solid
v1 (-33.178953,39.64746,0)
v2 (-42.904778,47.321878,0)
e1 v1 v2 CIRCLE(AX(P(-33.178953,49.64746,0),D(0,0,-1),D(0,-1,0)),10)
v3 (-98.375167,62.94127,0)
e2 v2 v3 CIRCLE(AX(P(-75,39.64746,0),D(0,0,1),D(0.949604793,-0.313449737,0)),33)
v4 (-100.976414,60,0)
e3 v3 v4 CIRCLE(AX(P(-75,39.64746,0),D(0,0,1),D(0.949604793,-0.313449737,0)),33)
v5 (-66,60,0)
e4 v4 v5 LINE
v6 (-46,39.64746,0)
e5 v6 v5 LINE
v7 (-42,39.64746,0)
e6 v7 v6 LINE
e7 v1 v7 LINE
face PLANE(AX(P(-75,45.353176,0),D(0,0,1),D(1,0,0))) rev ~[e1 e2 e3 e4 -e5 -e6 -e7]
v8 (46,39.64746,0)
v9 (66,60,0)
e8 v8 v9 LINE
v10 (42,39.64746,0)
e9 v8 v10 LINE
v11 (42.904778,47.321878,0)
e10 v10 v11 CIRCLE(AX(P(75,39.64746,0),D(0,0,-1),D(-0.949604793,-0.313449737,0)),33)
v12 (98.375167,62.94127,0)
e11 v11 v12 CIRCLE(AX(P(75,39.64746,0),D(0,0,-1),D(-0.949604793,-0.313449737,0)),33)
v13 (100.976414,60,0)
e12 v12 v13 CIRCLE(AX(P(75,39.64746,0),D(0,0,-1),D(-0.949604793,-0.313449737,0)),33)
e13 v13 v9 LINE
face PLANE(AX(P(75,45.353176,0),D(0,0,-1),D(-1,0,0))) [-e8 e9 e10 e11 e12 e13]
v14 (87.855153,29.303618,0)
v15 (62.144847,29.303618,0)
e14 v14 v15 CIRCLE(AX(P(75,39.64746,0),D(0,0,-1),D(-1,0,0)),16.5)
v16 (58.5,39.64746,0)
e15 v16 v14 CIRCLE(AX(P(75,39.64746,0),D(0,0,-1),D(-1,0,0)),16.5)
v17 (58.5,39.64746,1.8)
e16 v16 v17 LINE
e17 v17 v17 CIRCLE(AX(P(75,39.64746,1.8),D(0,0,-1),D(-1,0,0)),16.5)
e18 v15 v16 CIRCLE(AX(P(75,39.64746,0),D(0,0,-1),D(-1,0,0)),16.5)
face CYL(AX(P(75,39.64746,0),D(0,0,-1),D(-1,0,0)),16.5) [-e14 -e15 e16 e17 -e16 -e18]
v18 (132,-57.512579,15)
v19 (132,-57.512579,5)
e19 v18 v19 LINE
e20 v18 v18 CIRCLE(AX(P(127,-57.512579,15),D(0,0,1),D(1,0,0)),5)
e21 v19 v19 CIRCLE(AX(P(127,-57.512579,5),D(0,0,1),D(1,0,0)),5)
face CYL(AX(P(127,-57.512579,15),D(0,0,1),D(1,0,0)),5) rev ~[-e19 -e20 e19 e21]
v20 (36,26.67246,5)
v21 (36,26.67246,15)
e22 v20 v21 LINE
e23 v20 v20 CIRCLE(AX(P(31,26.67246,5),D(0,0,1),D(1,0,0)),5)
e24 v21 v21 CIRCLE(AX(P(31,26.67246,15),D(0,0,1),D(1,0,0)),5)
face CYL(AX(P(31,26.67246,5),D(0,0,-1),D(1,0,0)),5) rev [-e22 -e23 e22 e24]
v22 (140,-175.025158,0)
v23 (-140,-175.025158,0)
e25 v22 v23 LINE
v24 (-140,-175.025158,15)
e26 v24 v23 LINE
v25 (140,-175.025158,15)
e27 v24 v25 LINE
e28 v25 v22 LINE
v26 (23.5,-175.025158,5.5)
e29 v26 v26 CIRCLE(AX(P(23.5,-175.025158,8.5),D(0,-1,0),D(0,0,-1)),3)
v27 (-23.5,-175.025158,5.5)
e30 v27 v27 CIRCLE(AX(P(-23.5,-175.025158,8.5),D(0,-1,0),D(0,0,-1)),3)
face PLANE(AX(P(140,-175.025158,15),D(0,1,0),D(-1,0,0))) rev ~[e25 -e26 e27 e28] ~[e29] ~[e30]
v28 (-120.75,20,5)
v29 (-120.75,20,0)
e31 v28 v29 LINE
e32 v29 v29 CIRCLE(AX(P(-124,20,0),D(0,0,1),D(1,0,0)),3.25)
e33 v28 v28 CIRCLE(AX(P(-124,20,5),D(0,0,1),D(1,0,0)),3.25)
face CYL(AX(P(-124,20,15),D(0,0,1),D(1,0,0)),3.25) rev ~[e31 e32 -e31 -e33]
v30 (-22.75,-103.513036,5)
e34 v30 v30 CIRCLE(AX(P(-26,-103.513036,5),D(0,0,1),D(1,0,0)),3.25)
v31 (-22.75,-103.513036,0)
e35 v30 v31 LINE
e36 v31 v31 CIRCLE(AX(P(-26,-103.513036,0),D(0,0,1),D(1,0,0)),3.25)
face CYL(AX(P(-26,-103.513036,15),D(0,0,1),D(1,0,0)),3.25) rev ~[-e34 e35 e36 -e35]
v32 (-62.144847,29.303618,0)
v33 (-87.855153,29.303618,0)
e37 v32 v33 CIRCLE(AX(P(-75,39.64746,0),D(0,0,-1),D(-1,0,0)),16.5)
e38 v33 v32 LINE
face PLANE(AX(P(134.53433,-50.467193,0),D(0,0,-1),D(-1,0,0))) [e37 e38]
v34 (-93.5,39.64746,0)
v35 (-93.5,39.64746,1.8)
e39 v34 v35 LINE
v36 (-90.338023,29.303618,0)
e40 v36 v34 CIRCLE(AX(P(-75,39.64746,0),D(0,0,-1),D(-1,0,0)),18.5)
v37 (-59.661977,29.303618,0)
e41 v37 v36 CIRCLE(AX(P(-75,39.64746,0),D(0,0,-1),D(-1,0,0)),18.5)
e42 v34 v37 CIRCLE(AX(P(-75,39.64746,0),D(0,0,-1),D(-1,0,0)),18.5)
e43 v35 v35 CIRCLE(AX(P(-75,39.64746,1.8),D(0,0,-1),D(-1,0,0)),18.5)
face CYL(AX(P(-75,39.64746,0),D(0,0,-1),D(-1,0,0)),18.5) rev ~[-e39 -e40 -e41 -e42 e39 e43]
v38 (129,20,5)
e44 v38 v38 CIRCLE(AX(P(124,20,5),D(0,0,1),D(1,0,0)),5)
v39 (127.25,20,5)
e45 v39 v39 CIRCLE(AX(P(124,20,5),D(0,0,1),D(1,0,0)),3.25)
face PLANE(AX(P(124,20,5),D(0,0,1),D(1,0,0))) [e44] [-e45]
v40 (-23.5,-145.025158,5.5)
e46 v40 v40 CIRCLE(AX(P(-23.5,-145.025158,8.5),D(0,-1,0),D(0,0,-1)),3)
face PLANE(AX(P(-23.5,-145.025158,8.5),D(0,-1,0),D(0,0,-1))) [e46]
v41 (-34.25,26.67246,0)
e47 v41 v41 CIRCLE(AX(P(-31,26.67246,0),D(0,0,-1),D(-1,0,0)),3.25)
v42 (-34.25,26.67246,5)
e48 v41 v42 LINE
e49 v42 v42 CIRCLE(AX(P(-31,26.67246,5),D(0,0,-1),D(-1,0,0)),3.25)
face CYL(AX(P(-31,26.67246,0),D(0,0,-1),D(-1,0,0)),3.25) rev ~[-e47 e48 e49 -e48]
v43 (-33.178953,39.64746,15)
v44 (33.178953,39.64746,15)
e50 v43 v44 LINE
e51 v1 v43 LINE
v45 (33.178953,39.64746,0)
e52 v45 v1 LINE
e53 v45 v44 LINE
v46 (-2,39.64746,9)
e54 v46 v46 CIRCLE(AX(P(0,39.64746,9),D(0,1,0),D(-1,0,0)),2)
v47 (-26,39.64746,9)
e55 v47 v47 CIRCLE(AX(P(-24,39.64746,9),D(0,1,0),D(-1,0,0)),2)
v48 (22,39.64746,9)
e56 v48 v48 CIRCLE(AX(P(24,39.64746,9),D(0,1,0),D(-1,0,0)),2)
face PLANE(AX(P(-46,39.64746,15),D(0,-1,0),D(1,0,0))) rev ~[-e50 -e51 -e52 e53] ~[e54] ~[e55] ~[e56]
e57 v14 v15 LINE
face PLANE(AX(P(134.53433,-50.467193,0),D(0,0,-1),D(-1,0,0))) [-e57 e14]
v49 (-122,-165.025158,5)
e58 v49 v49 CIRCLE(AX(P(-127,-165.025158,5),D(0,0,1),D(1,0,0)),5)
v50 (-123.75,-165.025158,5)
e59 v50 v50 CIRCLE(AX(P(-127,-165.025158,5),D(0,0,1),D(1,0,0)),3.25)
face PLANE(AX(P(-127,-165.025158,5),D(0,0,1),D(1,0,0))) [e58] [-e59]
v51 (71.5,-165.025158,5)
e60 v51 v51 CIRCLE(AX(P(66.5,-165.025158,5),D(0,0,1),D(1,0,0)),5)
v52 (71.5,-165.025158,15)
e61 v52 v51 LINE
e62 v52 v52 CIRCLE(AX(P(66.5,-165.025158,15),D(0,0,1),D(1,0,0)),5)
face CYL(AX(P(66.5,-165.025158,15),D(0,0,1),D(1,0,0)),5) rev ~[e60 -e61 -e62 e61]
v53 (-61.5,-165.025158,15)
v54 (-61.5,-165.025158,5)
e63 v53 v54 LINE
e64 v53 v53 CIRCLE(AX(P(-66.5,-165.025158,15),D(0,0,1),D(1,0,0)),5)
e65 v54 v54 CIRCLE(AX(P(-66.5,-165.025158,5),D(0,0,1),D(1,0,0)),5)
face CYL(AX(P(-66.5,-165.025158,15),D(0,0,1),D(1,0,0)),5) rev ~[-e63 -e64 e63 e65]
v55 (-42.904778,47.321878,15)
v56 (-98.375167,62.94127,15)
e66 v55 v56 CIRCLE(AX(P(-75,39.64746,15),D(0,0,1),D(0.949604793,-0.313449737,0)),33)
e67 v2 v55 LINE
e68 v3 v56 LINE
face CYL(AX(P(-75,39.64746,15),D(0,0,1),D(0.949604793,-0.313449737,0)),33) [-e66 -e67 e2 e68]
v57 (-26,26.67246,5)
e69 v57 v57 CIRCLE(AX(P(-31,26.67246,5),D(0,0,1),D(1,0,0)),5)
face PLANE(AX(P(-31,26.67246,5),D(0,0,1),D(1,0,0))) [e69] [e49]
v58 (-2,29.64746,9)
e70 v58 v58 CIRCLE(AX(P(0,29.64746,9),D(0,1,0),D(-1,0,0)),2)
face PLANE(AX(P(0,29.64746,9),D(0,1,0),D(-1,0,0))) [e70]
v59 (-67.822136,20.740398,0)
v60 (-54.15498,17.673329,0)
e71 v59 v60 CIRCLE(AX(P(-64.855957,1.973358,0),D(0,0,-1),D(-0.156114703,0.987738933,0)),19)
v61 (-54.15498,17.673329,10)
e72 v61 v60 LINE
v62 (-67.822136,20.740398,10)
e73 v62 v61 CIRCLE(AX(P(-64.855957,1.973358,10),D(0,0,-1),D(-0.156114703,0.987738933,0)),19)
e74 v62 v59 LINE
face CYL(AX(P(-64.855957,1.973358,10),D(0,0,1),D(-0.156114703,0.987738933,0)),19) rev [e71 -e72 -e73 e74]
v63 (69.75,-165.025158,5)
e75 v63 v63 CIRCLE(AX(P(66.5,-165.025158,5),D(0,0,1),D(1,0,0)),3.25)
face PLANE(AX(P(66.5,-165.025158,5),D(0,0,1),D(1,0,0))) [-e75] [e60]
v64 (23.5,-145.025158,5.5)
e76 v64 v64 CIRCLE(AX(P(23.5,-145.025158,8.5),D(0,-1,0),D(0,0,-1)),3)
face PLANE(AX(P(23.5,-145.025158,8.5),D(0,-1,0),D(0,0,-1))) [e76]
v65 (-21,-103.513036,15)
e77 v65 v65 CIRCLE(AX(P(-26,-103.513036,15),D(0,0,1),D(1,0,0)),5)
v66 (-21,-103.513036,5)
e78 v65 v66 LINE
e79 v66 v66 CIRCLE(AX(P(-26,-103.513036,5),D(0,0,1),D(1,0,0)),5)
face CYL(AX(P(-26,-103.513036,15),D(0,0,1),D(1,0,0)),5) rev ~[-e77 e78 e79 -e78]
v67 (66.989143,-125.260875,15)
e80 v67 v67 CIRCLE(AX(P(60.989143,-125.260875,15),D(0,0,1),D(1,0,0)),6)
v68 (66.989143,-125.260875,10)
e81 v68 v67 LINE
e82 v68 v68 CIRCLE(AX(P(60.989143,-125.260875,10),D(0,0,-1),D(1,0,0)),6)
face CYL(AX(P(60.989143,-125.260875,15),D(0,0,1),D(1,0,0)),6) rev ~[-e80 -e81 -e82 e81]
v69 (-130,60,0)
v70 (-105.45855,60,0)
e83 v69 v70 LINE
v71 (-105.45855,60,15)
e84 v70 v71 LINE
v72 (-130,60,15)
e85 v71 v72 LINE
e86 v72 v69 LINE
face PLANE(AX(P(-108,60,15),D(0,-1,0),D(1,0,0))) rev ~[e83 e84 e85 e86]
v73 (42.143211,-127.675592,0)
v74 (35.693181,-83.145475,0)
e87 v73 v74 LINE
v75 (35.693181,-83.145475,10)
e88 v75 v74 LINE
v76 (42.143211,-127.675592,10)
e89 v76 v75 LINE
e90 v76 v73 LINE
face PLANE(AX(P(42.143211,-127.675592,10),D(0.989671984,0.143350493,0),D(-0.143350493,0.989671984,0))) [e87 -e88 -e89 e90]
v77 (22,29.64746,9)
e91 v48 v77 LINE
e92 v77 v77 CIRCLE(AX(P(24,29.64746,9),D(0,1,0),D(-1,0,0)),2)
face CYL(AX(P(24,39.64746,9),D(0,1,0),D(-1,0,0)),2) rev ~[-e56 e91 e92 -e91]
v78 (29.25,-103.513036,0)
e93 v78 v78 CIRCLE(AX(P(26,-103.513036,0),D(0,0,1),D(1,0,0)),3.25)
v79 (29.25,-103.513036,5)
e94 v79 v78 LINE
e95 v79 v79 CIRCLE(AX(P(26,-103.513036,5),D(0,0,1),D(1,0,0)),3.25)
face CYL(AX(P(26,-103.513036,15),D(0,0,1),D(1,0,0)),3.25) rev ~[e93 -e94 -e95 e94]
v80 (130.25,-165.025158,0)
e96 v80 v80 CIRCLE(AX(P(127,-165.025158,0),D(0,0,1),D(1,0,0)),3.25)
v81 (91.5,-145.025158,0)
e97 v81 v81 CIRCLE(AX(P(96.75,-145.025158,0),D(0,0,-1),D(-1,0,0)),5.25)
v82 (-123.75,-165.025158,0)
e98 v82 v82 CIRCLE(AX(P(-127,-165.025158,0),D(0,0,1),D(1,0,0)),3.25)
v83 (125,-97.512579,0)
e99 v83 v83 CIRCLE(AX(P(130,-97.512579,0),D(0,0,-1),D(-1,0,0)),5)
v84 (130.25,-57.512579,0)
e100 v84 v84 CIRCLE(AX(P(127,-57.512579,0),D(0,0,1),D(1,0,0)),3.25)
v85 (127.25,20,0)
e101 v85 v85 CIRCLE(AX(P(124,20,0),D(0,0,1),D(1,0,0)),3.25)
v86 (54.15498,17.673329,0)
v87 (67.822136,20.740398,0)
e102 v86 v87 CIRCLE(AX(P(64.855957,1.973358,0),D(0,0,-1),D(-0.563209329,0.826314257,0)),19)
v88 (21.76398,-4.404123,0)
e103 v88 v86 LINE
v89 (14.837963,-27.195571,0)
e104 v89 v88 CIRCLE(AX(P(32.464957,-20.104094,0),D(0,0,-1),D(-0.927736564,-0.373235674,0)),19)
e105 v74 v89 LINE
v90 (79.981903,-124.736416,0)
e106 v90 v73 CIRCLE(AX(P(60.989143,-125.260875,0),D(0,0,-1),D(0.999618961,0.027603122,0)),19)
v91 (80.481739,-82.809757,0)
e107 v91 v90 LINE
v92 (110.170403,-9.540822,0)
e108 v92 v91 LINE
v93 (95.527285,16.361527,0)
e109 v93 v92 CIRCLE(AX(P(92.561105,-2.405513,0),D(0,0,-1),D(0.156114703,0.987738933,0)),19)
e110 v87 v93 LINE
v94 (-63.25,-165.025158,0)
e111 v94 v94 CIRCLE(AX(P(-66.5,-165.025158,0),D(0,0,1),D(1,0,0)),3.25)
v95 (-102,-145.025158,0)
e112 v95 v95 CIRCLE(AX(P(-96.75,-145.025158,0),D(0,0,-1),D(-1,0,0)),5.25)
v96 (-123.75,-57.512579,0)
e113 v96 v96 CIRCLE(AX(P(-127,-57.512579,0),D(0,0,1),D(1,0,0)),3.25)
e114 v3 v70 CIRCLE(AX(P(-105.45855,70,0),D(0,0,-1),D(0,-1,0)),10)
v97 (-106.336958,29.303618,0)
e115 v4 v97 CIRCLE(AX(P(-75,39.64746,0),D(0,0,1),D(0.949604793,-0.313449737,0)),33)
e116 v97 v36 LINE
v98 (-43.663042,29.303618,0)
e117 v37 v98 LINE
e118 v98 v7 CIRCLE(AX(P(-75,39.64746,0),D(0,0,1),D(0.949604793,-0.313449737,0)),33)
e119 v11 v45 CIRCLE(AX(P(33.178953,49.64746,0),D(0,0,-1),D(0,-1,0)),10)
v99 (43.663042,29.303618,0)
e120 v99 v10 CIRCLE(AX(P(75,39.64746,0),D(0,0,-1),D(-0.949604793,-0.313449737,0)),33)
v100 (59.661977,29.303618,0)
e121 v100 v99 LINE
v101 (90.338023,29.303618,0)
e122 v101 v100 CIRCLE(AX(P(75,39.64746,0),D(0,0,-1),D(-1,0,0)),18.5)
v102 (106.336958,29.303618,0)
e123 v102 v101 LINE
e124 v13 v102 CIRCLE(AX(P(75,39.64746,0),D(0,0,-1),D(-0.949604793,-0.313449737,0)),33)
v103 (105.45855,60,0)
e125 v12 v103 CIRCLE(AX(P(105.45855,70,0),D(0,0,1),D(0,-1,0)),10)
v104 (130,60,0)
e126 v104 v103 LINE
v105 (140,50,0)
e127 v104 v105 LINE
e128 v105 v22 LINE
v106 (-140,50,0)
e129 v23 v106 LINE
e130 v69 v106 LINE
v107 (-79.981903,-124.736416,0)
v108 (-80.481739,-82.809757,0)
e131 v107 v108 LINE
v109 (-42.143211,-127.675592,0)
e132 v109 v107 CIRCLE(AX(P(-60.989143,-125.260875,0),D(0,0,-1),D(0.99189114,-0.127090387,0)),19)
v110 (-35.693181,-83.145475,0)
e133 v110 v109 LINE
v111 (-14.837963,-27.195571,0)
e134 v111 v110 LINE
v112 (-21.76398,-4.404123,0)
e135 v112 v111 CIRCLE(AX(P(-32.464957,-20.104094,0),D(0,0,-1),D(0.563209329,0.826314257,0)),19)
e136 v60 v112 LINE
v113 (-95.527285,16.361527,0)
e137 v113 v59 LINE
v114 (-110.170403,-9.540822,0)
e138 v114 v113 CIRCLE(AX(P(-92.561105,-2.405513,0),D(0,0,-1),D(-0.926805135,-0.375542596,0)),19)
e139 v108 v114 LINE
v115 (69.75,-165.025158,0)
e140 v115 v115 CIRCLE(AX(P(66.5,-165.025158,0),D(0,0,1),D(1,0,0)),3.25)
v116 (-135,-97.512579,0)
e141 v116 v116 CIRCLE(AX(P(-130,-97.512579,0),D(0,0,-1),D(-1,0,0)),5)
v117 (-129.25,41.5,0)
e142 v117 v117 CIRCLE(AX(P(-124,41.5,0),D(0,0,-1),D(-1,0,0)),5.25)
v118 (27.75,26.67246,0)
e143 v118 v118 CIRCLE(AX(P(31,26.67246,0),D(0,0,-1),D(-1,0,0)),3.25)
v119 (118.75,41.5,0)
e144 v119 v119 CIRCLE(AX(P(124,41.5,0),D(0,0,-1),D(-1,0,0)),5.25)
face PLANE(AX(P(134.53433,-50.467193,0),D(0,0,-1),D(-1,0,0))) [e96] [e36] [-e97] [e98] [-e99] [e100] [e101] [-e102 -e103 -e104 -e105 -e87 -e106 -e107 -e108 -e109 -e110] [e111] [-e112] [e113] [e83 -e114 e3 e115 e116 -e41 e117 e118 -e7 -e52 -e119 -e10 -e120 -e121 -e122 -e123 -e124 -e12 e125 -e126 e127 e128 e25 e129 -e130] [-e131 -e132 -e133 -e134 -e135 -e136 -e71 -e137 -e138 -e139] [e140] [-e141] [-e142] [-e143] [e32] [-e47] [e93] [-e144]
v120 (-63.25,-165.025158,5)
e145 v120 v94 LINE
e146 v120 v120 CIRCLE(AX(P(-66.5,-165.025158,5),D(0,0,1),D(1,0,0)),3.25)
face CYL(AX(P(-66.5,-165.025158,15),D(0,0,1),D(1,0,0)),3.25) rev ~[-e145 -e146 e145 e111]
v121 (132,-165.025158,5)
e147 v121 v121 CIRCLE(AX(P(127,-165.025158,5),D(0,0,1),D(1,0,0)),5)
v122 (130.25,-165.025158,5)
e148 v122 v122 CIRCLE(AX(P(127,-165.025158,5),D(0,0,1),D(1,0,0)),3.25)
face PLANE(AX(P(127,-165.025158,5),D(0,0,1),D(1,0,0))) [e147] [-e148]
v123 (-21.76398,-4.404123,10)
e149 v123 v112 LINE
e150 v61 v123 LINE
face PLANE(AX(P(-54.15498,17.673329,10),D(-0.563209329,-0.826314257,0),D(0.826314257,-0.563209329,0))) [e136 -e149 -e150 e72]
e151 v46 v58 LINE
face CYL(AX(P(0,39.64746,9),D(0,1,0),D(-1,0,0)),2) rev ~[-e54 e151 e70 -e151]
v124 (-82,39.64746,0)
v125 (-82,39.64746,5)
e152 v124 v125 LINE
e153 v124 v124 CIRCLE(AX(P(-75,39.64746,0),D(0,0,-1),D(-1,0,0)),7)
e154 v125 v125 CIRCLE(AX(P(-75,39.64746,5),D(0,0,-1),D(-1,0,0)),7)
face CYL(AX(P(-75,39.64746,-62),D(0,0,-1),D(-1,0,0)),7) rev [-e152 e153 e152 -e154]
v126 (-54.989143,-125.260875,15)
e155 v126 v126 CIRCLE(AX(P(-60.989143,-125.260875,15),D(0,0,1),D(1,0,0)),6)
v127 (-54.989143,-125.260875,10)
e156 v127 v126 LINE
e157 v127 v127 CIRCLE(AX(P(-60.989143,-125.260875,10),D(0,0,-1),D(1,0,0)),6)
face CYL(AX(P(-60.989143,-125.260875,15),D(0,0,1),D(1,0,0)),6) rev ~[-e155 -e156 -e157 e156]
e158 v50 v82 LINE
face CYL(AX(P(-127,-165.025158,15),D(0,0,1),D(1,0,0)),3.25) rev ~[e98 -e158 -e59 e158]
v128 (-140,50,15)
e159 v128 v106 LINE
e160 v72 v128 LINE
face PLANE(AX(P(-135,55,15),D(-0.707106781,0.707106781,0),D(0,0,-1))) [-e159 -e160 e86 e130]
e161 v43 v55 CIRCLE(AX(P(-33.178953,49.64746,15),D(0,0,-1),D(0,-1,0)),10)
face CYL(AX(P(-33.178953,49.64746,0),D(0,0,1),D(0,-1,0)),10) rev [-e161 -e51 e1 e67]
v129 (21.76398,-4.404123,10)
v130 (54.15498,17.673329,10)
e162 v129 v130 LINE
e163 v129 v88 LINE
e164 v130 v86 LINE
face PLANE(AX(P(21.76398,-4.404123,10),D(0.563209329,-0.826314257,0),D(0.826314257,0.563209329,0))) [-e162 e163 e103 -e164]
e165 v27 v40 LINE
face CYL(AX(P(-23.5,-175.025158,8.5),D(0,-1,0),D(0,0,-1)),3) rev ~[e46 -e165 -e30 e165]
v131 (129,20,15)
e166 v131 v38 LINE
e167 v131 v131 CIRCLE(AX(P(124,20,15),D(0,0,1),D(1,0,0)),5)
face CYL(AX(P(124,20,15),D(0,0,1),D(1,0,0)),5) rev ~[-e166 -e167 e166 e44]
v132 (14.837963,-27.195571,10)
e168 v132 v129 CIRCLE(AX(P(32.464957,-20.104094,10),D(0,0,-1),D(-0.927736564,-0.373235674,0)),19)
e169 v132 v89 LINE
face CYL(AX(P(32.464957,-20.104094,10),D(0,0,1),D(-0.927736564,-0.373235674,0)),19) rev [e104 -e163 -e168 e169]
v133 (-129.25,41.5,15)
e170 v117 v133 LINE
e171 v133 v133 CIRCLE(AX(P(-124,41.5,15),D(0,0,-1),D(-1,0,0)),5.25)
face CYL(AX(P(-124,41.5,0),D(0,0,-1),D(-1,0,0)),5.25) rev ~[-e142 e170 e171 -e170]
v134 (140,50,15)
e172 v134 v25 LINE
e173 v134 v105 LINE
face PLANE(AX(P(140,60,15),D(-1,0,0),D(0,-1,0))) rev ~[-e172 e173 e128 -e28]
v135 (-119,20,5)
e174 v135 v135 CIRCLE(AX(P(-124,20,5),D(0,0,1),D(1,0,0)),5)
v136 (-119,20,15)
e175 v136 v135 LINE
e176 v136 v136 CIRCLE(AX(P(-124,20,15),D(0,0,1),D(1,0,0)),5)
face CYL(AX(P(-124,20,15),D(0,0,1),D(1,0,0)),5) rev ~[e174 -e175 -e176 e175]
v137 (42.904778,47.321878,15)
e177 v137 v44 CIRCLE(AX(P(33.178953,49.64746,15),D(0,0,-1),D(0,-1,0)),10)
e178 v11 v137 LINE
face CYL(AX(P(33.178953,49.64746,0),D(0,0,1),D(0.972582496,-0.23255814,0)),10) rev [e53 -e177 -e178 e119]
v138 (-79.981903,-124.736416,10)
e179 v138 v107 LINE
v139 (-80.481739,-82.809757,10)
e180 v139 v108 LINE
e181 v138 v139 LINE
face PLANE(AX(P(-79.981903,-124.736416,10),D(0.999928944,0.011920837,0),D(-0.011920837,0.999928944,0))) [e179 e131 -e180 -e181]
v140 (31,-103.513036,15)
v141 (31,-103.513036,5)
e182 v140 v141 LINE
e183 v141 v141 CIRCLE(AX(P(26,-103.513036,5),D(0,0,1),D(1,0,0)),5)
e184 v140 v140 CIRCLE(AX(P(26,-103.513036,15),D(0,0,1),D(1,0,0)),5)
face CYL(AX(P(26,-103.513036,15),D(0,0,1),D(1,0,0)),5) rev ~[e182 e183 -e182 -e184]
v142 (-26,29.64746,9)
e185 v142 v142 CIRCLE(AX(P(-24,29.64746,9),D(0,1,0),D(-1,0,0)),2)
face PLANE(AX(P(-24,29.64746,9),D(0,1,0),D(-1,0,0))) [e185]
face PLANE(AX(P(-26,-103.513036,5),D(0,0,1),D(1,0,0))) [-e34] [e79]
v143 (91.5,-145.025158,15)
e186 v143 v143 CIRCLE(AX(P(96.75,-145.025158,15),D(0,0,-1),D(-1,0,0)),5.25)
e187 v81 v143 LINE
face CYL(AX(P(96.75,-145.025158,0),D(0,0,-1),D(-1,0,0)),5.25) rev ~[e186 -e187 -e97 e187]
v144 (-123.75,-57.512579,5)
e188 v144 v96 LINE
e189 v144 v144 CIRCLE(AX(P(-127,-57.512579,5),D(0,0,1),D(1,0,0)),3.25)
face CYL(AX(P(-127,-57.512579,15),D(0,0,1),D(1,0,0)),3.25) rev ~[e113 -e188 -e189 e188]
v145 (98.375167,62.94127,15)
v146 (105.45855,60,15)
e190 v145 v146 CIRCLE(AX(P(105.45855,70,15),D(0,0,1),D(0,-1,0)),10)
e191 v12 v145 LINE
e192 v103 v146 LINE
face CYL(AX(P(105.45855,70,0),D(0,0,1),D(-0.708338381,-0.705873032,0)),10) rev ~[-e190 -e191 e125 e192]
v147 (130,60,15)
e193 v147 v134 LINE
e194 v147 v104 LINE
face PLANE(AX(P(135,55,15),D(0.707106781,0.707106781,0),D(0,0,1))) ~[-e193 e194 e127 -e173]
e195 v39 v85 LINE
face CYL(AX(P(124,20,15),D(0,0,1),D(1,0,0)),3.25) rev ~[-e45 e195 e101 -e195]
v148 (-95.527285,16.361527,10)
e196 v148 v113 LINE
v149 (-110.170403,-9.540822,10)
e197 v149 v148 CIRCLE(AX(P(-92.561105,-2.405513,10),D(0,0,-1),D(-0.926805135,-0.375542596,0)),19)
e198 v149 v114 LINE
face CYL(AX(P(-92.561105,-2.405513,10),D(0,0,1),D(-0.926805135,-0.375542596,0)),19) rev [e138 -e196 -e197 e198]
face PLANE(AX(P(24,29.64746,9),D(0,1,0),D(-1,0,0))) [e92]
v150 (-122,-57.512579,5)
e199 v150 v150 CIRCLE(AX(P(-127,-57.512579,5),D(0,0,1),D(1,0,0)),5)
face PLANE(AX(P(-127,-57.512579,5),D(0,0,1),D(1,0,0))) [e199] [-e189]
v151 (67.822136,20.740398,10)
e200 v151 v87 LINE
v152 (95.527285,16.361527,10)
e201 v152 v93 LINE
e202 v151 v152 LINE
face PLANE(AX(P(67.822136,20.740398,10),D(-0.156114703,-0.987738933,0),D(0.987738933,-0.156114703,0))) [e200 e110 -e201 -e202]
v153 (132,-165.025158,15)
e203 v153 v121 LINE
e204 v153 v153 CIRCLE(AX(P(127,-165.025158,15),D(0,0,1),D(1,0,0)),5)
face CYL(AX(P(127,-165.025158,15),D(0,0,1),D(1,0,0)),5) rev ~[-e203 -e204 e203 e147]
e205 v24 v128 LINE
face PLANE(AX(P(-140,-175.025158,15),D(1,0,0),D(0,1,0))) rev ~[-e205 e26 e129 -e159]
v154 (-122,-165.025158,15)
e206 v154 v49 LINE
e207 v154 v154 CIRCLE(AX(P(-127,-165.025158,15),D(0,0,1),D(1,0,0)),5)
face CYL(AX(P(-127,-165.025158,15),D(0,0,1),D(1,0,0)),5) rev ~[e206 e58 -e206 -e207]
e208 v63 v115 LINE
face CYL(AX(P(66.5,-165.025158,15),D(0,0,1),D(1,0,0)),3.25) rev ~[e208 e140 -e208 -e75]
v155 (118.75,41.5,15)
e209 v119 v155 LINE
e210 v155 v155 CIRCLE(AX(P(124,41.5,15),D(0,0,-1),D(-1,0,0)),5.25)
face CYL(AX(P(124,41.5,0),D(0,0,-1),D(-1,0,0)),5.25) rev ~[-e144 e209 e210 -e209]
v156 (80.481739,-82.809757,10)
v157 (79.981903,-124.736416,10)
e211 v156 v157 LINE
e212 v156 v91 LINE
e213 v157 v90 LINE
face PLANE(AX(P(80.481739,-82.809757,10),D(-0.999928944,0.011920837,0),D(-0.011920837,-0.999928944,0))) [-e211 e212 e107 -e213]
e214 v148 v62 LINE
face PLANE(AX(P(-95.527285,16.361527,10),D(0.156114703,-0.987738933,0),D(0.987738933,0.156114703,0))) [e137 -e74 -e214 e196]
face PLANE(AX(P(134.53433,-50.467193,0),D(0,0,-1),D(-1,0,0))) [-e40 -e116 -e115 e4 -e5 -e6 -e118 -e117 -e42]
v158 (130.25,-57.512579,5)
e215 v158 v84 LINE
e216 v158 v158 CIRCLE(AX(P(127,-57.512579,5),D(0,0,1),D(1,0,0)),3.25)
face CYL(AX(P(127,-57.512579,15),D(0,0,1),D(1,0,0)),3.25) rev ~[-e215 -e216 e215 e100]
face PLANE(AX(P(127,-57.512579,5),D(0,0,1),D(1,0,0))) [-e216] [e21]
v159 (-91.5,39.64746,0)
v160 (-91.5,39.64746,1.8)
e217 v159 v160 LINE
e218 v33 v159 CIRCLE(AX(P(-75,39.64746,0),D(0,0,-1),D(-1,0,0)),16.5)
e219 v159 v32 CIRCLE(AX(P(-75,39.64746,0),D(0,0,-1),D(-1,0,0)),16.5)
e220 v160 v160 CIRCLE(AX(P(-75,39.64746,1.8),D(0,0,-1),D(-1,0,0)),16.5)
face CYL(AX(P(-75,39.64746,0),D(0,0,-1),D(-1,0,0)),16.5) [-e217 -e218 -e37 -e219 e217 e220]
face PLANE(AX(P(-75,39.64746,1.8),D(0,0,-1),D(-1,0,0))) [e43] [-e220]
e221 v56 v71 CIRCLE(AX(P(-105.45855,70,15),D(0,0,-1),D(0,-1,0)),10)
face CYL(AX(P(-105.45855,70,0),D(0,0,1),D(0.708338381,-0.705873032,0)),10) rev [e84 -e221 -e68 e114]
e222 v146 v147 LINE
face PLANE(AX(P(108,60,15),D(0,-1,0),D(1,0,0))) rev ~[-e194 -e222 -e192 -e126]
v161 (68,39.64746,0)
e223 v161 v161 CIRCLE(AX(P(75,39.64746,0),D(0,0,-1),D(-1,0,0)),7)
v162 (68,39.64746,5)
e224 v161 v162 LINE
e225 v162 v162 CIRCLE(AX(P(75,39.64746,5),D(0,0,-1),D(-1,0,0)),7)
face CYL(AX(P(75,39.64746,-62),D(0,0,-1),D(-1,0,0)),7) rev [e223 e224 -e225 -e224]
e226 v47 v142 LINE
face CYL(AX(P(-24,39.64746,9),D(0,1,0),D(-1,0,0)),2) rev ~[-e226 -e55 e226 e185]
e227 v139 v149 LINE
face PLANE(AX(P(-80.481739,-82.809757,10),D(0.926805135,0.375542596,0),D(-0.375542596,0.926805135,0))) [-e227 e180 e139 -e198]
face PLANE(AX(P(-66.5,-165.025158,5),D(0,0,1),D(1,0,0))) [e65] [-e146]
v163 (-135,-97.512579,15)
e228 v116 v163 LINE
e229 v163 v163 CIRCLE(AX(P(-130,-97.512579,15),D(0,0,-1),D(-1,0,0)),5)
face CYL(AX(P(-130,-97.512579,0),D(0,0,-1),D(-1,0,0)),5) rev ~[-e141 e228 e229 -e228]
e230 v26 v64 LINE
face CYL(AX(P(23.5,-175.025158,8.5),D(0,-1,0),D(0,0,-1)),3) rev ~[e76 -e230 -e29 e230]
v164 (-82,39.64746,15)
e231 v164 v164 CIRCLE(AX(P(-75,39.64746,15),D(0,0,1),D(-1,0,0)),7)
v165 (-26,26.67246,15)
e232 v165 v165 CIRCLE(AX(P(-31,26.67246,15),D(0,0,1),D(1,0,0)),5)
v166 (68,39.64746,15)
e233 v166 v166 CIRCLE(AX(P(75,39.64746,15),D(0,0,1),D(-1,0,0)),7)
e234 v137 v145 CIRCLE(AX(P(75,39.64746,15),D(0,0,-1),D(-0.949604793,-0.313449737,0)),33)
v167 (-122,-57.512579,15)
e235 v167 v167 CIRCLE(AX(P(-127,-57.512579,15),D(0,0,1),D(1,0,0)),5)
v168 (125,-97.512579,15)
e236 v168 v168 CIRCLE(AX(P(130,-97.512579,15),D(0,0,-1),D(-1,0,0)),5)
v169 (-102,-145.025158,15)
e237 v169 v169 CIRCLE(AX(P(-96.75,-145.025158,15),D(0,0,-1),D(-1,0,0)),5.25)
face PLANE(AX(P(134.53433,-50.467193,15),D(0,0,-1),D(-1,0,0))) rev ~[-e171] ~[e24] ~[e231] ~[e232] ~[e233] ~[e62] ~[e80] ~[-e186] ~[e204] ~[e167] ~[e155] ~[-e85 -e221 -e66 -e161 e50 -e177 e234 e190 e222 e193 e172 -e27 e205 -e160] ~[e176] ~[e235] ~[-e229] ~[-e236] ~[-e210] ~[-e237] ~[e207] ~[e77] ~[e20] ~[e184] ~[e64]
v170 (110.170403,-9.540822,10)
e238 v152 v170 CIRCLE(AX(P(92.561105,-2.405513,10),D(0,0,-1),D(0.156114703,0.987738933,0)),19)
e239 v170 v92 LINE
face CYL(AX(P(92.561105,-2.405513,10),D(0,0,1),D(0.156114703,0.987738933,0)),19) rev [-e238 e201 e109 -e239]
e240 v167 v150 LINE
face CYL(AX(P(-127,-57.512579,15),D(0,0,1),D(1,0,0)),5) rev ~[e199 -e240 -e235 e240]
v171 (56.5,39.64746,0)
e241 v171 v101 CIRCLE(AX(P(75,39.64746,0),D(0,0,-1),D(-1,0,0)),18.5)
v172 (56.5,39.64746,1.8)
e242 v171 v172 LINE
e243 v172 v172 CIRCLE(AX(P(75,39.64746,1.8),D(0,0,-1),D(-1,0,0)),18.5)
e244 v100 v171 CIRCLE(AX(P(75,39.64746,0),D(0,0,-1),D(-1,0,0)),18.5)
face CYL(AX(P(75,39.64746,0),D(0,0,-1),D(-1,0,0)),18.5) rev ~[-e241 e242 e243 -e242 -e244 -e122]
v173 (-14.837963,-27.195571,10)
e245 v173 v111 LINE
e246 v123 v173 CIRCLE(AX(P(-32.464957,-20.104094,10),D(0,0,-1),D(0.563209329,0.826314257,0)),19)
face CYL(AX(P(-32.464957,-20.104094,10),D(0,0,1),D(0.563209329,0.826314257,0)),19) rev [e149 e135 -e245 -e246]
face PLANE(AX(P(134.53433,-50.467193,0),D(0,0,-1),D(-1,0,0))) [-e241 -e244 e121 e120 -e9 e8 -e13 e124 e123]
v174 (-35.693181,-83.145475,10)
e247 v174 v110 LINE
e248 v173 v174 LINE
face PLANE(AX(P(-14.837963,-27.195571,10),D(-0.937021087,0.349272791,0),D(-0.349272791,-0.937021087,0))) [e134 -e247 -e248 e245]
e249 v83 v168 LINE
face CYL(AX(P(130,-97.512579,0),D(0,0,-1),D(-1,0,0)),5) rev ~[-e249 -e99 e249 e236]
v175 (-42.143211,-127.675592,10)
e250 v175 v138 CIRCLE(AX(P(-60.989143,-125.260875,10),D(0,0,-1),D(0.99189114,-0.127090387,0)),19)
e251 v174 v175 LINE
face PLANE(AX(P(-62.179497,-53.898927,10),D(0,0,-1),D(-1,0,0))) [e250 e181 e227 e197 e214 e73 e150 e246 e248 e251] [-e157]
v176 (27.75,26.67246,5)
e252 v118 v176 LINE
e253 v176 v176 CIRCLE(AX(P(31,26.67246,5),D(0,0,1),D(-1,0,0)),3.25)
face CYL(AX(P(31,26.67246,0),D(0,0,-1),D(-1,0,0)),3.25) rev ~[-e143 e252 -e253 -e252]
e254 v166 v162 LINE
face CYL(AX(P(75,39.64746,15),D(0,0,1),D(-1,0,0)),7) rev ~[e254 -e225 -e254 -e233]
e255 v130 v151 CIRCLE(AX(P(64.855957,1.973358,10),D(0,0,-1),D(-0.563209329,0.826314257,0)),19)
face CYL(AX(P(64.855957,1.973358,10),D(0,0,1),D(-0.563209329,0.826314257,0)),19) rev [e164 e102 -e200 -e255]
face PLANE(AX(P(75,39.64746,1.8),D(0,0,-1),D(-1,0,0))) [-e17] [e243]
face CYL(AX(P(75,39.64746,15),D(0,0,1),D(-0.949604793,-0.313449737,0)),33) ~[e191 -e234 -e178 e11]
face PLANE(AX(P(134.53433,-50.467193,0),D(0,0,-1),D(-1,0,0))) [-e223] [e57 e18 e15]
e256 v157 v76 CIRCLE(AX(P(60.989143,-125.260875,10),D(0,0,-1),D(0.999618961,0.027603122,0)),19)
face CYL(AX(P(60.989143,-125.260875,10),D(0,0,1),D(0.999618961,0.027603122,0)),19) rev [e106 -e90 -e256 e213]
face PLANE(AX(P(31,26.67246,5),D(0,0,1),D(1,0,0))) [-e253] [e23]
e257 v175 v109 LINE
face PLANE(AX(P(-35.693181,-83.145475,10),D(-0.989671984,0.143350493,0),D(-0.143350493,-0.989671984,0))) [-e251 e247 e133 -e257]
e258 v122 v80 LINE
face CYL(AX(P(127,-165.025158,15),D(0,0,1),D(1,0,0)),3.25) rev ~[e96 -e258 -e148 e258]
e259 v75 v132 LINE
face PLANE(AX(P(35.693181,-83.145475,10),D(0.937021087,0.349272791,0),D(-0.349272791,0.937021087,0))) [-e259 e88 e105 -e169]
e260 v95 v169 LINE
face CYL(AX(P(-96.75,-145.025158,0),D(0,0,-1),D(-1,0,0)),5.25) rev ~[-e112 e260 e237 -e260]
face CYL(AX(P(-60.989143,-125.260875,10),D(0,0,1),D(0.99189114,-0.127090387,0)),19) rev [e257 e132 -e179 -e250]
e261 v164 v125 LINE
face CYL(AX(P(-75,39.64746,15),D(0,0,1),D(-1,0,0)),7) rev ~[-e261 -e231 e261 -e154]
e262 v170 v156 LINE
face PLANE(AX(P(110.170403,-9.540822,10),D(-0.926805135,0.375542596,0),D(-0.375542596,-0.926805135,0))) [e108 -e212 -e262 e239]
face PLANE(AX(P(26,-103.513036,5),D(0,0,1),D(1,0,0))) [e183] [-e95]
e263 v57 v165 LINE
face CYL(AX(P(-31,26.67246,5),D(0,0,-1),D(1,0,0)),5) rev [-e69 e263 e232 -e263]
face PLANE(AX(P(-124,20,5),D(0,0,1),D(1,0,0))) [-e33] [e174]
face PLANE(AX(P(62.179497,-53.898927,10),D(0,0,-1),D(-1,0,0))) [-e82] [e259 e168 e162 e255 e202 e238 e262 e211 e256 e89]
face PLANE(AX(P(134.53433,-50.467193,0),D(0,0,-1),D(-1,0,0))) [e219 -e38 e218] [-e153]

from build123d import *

# Parameters (mm, degrees)
BOSS_EXTRUDE1_DEPTH     = 5
SKETCH10_W              = 430.19860944
SKETCH10_H              = 431.937312902
SKETCH10_W_2            = 300
SKETCH10_H_2            = 230
CUT_EXTRUDE1_DEPTH      = 50
CUT_EXTRUDE2_DEPTH      = 34
CUT_EXTRUDE2_DEPTH_BACK = 67
SKETCH11_R              = 7
CUT_EXTRUDE3_DEPTH      = 83
CUT_EXTRUDE3_DEPTH_BACK = 62
SKETCH13_W              = 90
SKETCH13_H              = 26.63854706
CUT_EXTRUDE4_DEPTH      = 38
SKETCH16_R              = 6
CUT_EXTRUDE7_DEPTH      = 36
CUT_EXTRUDE8_DEPTH      = 10
BOSS_EXTRUDE2_DEPTH     = 10
SKETCH23_W              = 266
SKETCH23_H              = 30
BOSS_EXTRUDE5_DEPTH     = 15
SKETCH24_W              = 32
SKETCH24_H              = 53.383916467
CUT_EXTRUDE9_DEPTH      = 10
BOSS_EXTRUDE6_DEPTH     = 10
CUT_EXTRUDE10_DEPTH     = 56
CUT_EXTRUDE11_DEPTH     = 15
CUT_EXTRUDE12_DEPTH     = 10
BOSS_EXTRUDE7_START     = 10
SKETCH33_R              = 6
SKETCH33_R_2            = 7
BOSS_EXTRUDE7_DEPTH     = 10
CUT_EXTRUDE13_START     = -10
SKETCH32_R              = 6
CUT_EXTRUDE13_DEPTH     = 10
SKETCH34_R              = 3
CUT_EXTRUDE14_DEPTH     = 30
SKETCH36_R              = 3.25
CUT_EXTRUDE15_DEPTH     = 30
SKETCH37_R              = 5
CUT_EXTRUDE18_DEPTH     = 10
BOSS_EXTRUDE8_DEPTH     = 15
CHAMFER1_SIZE           = 10
SKETCH39_R              = 3.25
CUT_EXTRUDE19_DEPTH     = 143
CUT_EXTRUDE20_START     = -10
SKETCH40_R              = 5
SKETCH40_R_2            = 3.25
CUT_EXTRUDE20_DEPTH     = 10
SKETCH41_R              = 7
BOSS_EXTRUDE9_DEPTH     = 15
SKETCH42_R              = 5.25
CUT_EXTRUDE21_DEPTH     = 78
FILLET1_R               = 10
FILLET2_R               = 10
SKETCH43_R              = 3.25
CUT_EXTRUDE22_DEPTH     = 69
SKETCH44_R              = 5
CUT_EXTRUDE23_DEPTH     = 10
SKETCH45_R              = 5
CUT_EXTRUDE24_DEPTH     = 81
SKETCH46_R              = 2
CUT_EXTRUDE26_DEPTH     = 10
SKETCH47_R              = 18.5
SKETCH47_R_2            = 16.5
CUT_EXTRUDE27_DEPTH     = 1.8


with BuildPart() as part:
    # Sketch1 → Boss-Extrude1 (new body)
    with BuildSketch(Plane.XY):
        Polygon((-150, -150), (-150, -170), (150, -170), (150, -150), (150, 150), (-150, 150), align=None)
    extrude(amount=BOSS_EXTRUDE1_DEPTH)

    # Sketch10 → Cut-Extrude1 (cut)
    with BuildSketch(Plane.XY.offset(5)):
        Rectangle(SKETCH10_W, SKETCH10_H)
        with Locations((0, -55)):
            Rectangle(SKETCH10_W_2, SKETCH10_H_2, mode=Mode.SUBTRACT)
    extrude(amount=-CUT_EXTRUDE1_DEPTH, mode=Mode.SUBTRACT)

    # Sketch11 → Cut-Extrude2 (cut, two sides: drawn at the far end of the back side and taken through both)
    with BuildSketch(Plane.XY.offset(5).offset(-CUT_EXTRUDE2_DEPTH_BACK)):
        with Locations(Location((-75, 39.647459622, 0), (0, 0, 180))):
            Circle(SKETCH11_R)
        with Locations(Location((75, 39.647459622, 0), (0, 0, 180))):
            Circle(SKETCH11_R)
    extrude(amount=CUT_EXTRUDE2_DEPTH + CUT_EXTRUDE2_DEPTH_BACK, mode=Mode.SUBTRACT)

    # Sketch12 → Cut-Extrude3 (cut, two sides: drawn at the far end of the back side and taken through both)
    with BuildSketch(Plane.XY.offset(5).offset(-CUT_EXTRUDE3_DEPTH_BACK)):
        Polygon((-150, 60), (-133, 60), (-133, -183.341935532), (-188.985171206, -183.341935532), (-185.209913478, 60), align=None)
        Polygon((185.209913478, 60), (150, 60), (133, 60), (133, -183.341935532), (188.985171206, -183.341935532), align=None)
    extrude(amount=CUT_EXTRUDE3_DEPTH + CUT_EXTRUDE3_DEPTH_BACK, mode=Mode.SUBTRACT)

    # Sketch13 → Cut-Extrude4 (cut)
    with BuildSketch(Plane.XY.offset(5)):
        with Locations((0, 52.966733152)):
            Rectangle(SKETCH13_W, SKETCH13_H)
    extrude(amount=-CUT_EXTRUDE4_DEPTH, mode=Mode.SUBTRACT)

    # Sketch16 → Cut-Extrude7 (cut)
    with BuildSketch(Plane.XY.offset(5)):
        with Locations((-60.989142528, -125.260874967)):
            Circle(SKETCH16_R)
        with Locations((60.989142528, -125.260874967)):
            Circle(SKETCH16_R)
    extrude(amount=-CUT_EXTRUDE7_DEPTH, mode=Mode.SUBTRACT)

    # Sketch18 → Cut-Extrude8 (cut)
    with BuildSketch(Plane.XY.offset(5)):
        Polygon((-63.637907567, -145.025157671), (138.825867156, -145.025157671), (138.825867156, -178.761284058), (-147.679626059, -178.761284058), (-147.679626059, -145.025157671), align=None)
    extrude(amount=-CUT_EXTRUDE8_DEPTH, mode=Mode.SUBTRACT)

    # Sketch20 → Boss-Extrude2 (add)
    with BuildSketch(Plane.XY.offset(5)):
        Polygon((-119.231997115, -76.857332264), (-119.231997115, -50.797544119), (-130, -50.797544119), (-130, -19.723575517), (-108, -19.723575517), (-108, 60), (-133, 20), (-133, -145.025157671), (133, -145.025157671), (133, 20), (108, 60), (108, -19.723575517), (130, -19.723575517), (130, -50.797544119), (119.231997115, -50.797544119), (119.231997115, -76.857332264), (119.231997115, -125.260874967), (80.989142528, -125.260874967), (80.989142528, -142.025157671), (40.835190362, -142.025157671), (40.835190362, -125.260874967), (-40.835190362, -125.260874967), (-40.835190362, -142.025157671), (-80.989142528, -142.025157671), (-80.989142528, -125.260874967), (-119.231997115, -125.260874967), align=None)
    extrude(amount=BOSS_EXTRUDE2_DEPTH)

    # Sketch23 → Boss-Extrude5 (add)
    with BuildSketch(Plane.XY.offset(15)):
        with Locations((0, -160.025157671)):
            Rectangle(SKETCH23_W, SKETCH23_H)
    extrude(amount=-BOSS_EXTRUDE5_DEPTH)

    # Sketch24 → Cut-Extrude9 (cut)
    with BuildSketch(Plane.XY.offset(15)):
        with Locations((0, -151.952833201)):
            Rectangle(SKETCH24_W, SKETCH24_H)
    extrude(amount=-CUT_EXTRUDE9_DEPTH, mode=Mode.SUBTRACT)

    # Sketch25 → Boss-Extrude6 (add)
    with BuildSketch(Plane.XY.offset(15)):
        with BuildLine():
            Line((-77.989142528, -125.260874967), (-80.989142528, -125.260874967))
            Line((-80.989142528, -125.260874967), (-80.989142528, -142.025157671))
            Line((-80.989142528, -142.025157671), (-63.810281555, -142.025157671))
            ThreePointArc((-63.810281555, -142.025157671), (-73.969114859, -136.239049599), (-77.989142528, -125.260874967))
        make_face()
        with BuildLine():
            Line((-58.1680035, -142.025157671), (-40.835190362, -142.025157671))
            Line((-40.835190362, -142.025157671), (-40.835190362, -125.260874967))
            Line((-40.835190362, -125.260874967), (-43.989142528, -125.260874967))
            ThreePointArc((-43.989142528, -125.260874967), (-48.009170196, -136.239049599), (-58.1680035, -142.025157671))
        make_face()
        with BuildLine():
            Line((40.835190362, -125.260874967), (43.989142528, -125.260874967))
            ThreePointArc((43.989142528, -125.260874967), (48.009170196, -136.239049599), (58.1680035, -142.025157671))
            Line((58.1680035, -142.025157671), (40.835190362, -142.025157671))
            Line((40.835190362, -142.025157671), (40.835190362, -125.260874967))
        make_face()
        with BuildLine():
            Line((80.989142528, -142.025157671), (63.810281555, -142.025157671))
            ThreePointArc((63.810281555, -142.025157671), (73.969114859, -136.239049599), (77.989142528, -125.260874967))
            Line((77.989142528, -125.260874967), (80.989142528, -125.260874967))
            Line((80.989142528, -125.260874967), (80.989142528, -142.025157671))
        make_face()
    extrude(amount=-BOSS_EXTRUDE6_DEPTH)

    # Sketch28 → Cut-Extrude10 (cut)
    with BuildSketch(Plane.XY.offset(5)):
        Polygon((-46, 60), (-41.318426322, 60), (-41.318426322, 39.647459622), (-46, 39.647459622), (-66, 60), align=None)
        Polygon((41.318426322, 39.647459622), (46, 39.647459622), (66, 60), (46, 60), (41.318426322, 60), align=None)
    extrude(amount=-CUT_EXTRUDE10_DEPTH, mode=Mode.SUBTRACT)

    # Sketch29 → Cut-Extrude11 (cut)
    with BuildSketch(Plane.XY.offset(5)):
        Polygon((-133, 60), (-133, 20), (-108, 60), align=None)
        Polygon((108, 60), (133, 20), (133, 60), align=None)
    extrude(amount=-CUT_EXTRUDE11_DEPTH, mode=Mode.SUBTRACT)

    # Sketch31 → Cut-Extrude12 (cut)
    with BuildSketch(Plane.XY.offset(15)):
        Polygon((-108, 35), (-130, -19.723575517), (-94.809291049, -33.870962445), align=None)
        Polygon((108, 35), (130, -19.723575517), (80.731863312, -35.260559818), align=None)
    extrude(amount=-CUT_EXTRUDE12_DEPTH, mode=Mode.SUBTRACT)

    # Sketch33 → Boss-Extrude7 (add)
    with BuildSketch(Plane.XY.offset(5).offset(BOSS_EXTRUDE7_START)):
        Polygon((-66, 60), (-46, 39.647459622), (46, 39.647459622), (66, 60), (108, 60), (133, 20), (133, -175.025157671), (16, -175.025157671), (-16, -175.025157671), (-133, -175.025157671), (-133, 20), (-108, 60), align=None)
        with Locations((60.989142528, -125.260874967)):
            Circle(SKETCH33_R, mode=Mode.SUBTRACT)
        with Locations((-60.989142528, -125.260874967)):
            Circle(SKETCH33_R, mode=Mode.SUBTRACT)
        with Locations(Location((75, 39.647459622, 0), (0, 0, 180))):
            Circle(SKETCH33_R_2, mode=Mode.SUBTRACT)
        with Locations(Location((-75, 39.647459622, 0), (0, 0, 180))):
            Circle(SKETCH33_R_2, mode=Mode.SUBTRACT)
    extrude(amount=-BOSS_EXTRUDE7_DEPTH)

    # Sketch32 → Cut-Extrude13 (cut)
    # profile 1 of 2: a face of its own
    with BuildSketch(Plane(origin=(0, 0, 0), x_dir=(-1, 0, 0), z_dir=(0, 0, -1)).offset(CUT_EXTRUDE13_START)):
        with BuildLine():
            Line((-67.822136157, 20.740397673), (-95.527284672, 16.361527024))
            ThreePointArc((-95.527284672, 16.361527024), (-109.101071589, 6.94486247), (-110.170402891, -9.540822021))
            Line((-110.170402891, -9.540822021), (-80.481739168, -82.809756918))
            Line((-80.481739168, -82.809756918), (-79.981902791, -124.736415651))
            ThreePointArc((-79.981902791, -124.736415651), (-62.46056345, -144.203813505), (-42.143210868, -127.67559232))
            Line((-42.143210868, -127.67559232), (-35.693180555, -83.14547495))
            Line((-35.693180555, -83.14547495), (-14.837962686, -27.195571485))
            ThreePointArc((-14.837962686, -27.195571485), (-14.285820116, -14.579696177), (-21.763980146, -4.404122789))
            Line((-21.763980146, -4.404122789), (-54.154979556, 17.673328836))
            ThreePointArc((-54.154979556, 17.673328836), (-60.695607968, 20.512276405), (-67.822136157, 20.740397673))
        make_face()
        with Locations(Location((-60.989142528, -125.260874967, 0), (0, 0, 180))):
            Circle(SKETCH32_R, mode=Mode.SUBTRACT)
    # profile 2 of 2: a face of its own
    with BuildSketch(Plane(origin=(0, 0, 0), x_dir=(-1, 0, 0), z_dir=(0, 0, -1)).offset(CUT_EXTRUDE13_START)):
        with BuildLine():
            Line((54.154979556, 17.673328836), (21.763980146, -4.404122789))
            ThreePointArc((21.763980146, -4.404122789), (14.285820116, -14.579696177), (14.837962686, -27.195571485))
            Line((14.837962686, -27.195571485), (35.693180555, -83.14547495))
            Line((35.693180555, -83.14547495), (42.143210868, -127.67559232))
            ThreePointArc((42.143210868, -127.67559232), (62.46056345, -144.203813505), (79.981902791, -124.736415651))
            Line((79.981902791, -124.736415651), (80.481739168, -82.809756918))
            Line((80.481739168, -82.809756918), (110.170402891, -9.540822021))
            ThreePointArc((110.170402891, -9.540822021), (109.101071589, 6.94486247), (95.527284672, 16.361527024))
            Line((95.527284672, 16.361527024), (67.822136157, 20.740397673))
            ThreePointArc((67.822136157, 20.740397673), (60.695607968, 20.512276405), (54.154979556, 17.673328836))
        make_face()
        with Locations(Location((60.989142528, -125.260874967, 0), (0, 0, 180))):
            Circle(SKETCH32_R, mode=Mode.SUBTRACT)
    extrude(amount=CUT_EXTRUDE13_DEPTH, mode=Mode.SUBTRACT)

    # Sketch34 → Cut-Extrude14 (cut)
    with BuildSketch(Plane.XZ.offset(175.025157671)):
        with Locations(Location((23.5, 8.5, 0), (0, 0, 270))):
            Circle(SKETCH34_R)
        with Locations(Location((-23.5, 8.5, 0), (0, 0, 270))):
            Circle(SKETCH34_R)
    extrude(amount=-CUT_EXTRUDE14_DEPTH, mode=Mode.SUBTRACT)

    # Sketch36 → Cut-Extrude15 (cut)
    with BuildSketch(Plane.XY.offset(15)):
        with Locations((-124, 20)):
            Circle(SKETCH36_R)
        with Locations((-127, -57.512578835)):
            Circle(SKETCH36_R)
        with Locations((-127, -165.025157671)):
            Circle(SKETCH36_R)
        with Locations((-66.5, -165.025157671)):
            Circle(SKETCH36_R)
        with Locations((66.5, -165.025157671)):
            Circle(SKETCH36_R)
        with Locations((127, -165.025157671)):
            Circle(SKETCH36_R)
        with Locations((127, -57.512578835)):
            Circle(SKETCH36_R)
        with Locations((124, 20)):
            Circle(SKETCH36_R)
    extrude(amount=-CUT_EXTRUDE15_DEPTH, mode=Mode.SUBTRACT)

    # Sketch37 → Cut-Extrude18 (cut)
    with BuildSketch(Plane.XY.offset(15)):
        with Locations((-124, 20)):
            Circle(SKETCH37_R)
        with Locations((-127, -57.512578835)):
            Circle(SKETCH37_R)
        with Locations((-127, -165.025157671)):
            Circle(SKETCH37_R)
        with Locations((-66.5, -165.025157671)):
            Circle(SKETCH37_R)
        with Locations((66.5, -165.025157671)):
            Circle(SKETCH37_R)
        with Locations((127, -165.025157671)):
            Circle(SKETCH37_R)
        with Locations((127, -57.512578835)):
            Circle(SKETCH37_R)
        with Locations((124, 20)):
            Circle(SKETCH37_R)
    extrude(amount=-CUT_EXTRUDE18_DEPTH, mode=Mode.SUBTRACT)

    # Sketch38 → Boss-Extrude8 (add)
    with BuildSketch(Plane.XY.offset(15)):
        Polygon((108, 60), (140, 60), (140, -175.025157671), (133, -175.025157671), (133, 20), align=None)
        Polygon((-108, 60), (-133, 20), (-133, -175.025157671), (-140, -175.025157671), (-140, 60), align=None)
    extrude(amount=-BOSS_EXTRUDE8_DEPTH)

    # Chamfer1
    chamfer1_edges = [part.edges().sort_by_distance(p)[0] for p in [
        (140, 60, 7.5),
        (-140, 60, 7.5),
    ]]
    chamfer(chamfer1_edges, length=CHAMFER1_SIZE)

    # Sketch39 → Cut-Extrude19 (cut)
    with BuildSketch(Plane(origin=(0, 0, 0), x_dir=(-1, 0, 0), z_dir=(0, 0, -1))):
        with Locations((-31, 26.672459622)):
            Circle(SKETCH39_R)
        with Locations((31, 26.672459622)):
            Circle(SKETCH39_R)
    extrude(amount=-CUT_EXTRUDE19_DEPTH, mode=Mode.SUBTRACT)

    # Sketch40 → Cut-Extrude20 (cut)
    # profile 1 of 2: a face of its own
    with BuildSketch(Plane.XY.offset(15).offset(CUT_EXTRUDE20_START)):
        with Locations((31, 26.672459622)):
            Circle(SKETCH40_R)
        with Locations(Location((31, 26.672459622, 0), (0, 0, 180))):
            Circle(SKETCH40_R_2, mode=Mode.SUBTRACT)
    # profile 2 of 2: a face of its own
    with BuildSketch(Plane.XY.offset(15).offset(CUT_EXTRUDE20_START)):
        with Locations((-31, 26.672459622)):
            Circle(SKETCH40_R)
    extrude(amount=CUT_EXTRUDE20_DEPTH, mode=Mode.SUBTRACT)

    # Sketch41 → Boss-Extrude9 (add)
    # profile 1 of 2: a face of its own
    with BuildSketch(Plane.XY.offset(15)):
        with BuildLine():
            Line((106.336958161, 29.303618305), (43.663041839, 29.303618305))
            ThreePointArc((43.663041839, 29.303618305), (75, 72.647459622), (106.336958161, 29.303618305))
        make_face()
        with Locations(Location((75, 39.647459622, 0), (0, 0, 180))):
            Circle(SKETCH41_R, mode=Mode.SUBTRACT)
    # profile 2 of 2: a face of its own
    with BuildSketch(Plane.XY.offset(15)):
        with BuildLine():
            Line((-106.336958161, 29.303618305), (-43.663041839, 29.303618305))
            ThreePointArc((-43.663041839, 29.303618305), (-75, 72.647459622), (-106.336958161, 29.303618305))
        make_face()
        with Locations(Location((-75, 39.647459622, 0), (0, 0, 180))):
            Circle(SKETCH41_R, mode=Mode.SUBTRACT)
    extrude(amount=-BOSS_EXTRUDE9_DEPTH)

    # Sketch42 → Cut-Extrude21 (cut)
    with BuildSketch(Plane(origin=(0, 0, 0), x_dir=(-1, 0, 0), z_dir=(0, 0, -1))):
        with Locations((124, 41.5)):
            Circle(SKETCH42_R)
        with Locations((-124, 41.5)):
            Circle(SKETCH42_R)
        with Locations((-96.75, -145.025157671)):
            Circle(SKETCH42_R)
        with Locations((96.75, -145.025157671)):
            Circle(SKETCH42_R)
    extrude(amount=-CUT_EXTRUDE21_DEPTH, mode=Mode.SUBTRACT)

    # Fillet1
    fillet1_edges = [part.edges().sort_by_distance(p)[0] for p in [
        (42, 39.647459622, 7.5),
        (-42, 39.647459622, 7.5),
    ]]
    fillet(fillet1_edges, radius=FILLET1_R)

    # Fillet2
    fillet2_edges = [part.edges().sort_by_distance(p)[0] for p in [
        (100.976414305, 60, 7.5),
        (-100.976414305, 60, 7.5),
    ]]
    fillet(fillet2_edges, radius=FILLET2_R)

    # Sketch43 → Cut-Extrude22 (cut)
    with BuildSketch(Plane.XY.offset(15)):
        with Locations((26, -103.513035633)):
            Circle(SKETCH43_R)
        with Locations((-26, -103.513035633)):
            Circle(SKETCH43_R)
    extrude(amount=-CUT_EXTRUDE22_DEPTH, mode=Mode.SUBTRACT)

    # Sketch44 → Cut-Extrude23 (cut)
    with BuildSketch(Plane.XY.offset(15)):
        with Locations((-26, -103.513035633)):
            Circle(SKETCH44_R)
        with Locations((26, -103.513035633)):
            Circle(SKETCH44_R)
    extrude(amount=-CUT_EXTRUDE23_DEPTH, mode=Mode.SUBTRACT)

    # Sketch45 → Cut-Extrude24 (cut)
    with BuildSketch(Plane(origin=(0, 0, 0), x_dir=(-1, 0, 0), z_dir=(0, 0, -1))):
        with Locations((130.000000029, -97.512578887)):
            Circle(SKETCH45_R)
        with Locations((-129.999999971, -97.512578887)):
            Circle(SKETCH45_R)
    extrude(amount=-CUT_EXTRUDE24_DEPTH, mode=Mode.SUBTRACT)

    # Sketch46 → Cut-Extrude26 (cut)
    with BuildSketch(Plane(origin=(0, 39.647459622, 0), x_dir=(1, 0, 0), z_dir=(0, 1, 0))):
        with Locations(Location((-24, -9, 0), (0, 0, 180))):
            Circle(SKETCH46_R)
        with Locations(Location((0, -9, 0), (0, 0, 180))):
            Circle(SKETCH46_R)
        with Locations(Location((24, -9, 0), (0, 0, 180))):
            Circle(SKETCH46_R)
    extrude(amount=-CUT_EXTRUDE26_DEPTH, mode=Mode.SUBTRACT)

    # Sketch47 → Cut-Extrude27 (cut)
    # profile 1 of 2: a face of its own
    with BuildSketch(Plane(origin=(0, 0, 0), x_dir=(-1, 0, 0), z_dir=(0, 0, -1))):
        with Locations((-75, 39.647459622)):
            Circle(SKETCH47_R)
        with Locations((-75, 39.647459622)):
            Circle(SKETCH47_R_2, mode=Mode.SUBTRACT)
    # profile 2 of 2: a face of its own
    with BuildSketch(Plane(origin=(0, 0, 0), x_dir=(-1, 0, 0), z_dir=(0, 0, -1))):
        with Locations((75, 39.647459622)):
            Circle(SKETCH47_R)
        with Locations((75, 39.647459622)):
            Circle(SKETCH47_R_2, mode=Mode.SUBTRACT)
    extrude(amount=-CUT_EXTRUDE27_DEPTH, mode=Mode.SUBTRACT)


solid = part.part
